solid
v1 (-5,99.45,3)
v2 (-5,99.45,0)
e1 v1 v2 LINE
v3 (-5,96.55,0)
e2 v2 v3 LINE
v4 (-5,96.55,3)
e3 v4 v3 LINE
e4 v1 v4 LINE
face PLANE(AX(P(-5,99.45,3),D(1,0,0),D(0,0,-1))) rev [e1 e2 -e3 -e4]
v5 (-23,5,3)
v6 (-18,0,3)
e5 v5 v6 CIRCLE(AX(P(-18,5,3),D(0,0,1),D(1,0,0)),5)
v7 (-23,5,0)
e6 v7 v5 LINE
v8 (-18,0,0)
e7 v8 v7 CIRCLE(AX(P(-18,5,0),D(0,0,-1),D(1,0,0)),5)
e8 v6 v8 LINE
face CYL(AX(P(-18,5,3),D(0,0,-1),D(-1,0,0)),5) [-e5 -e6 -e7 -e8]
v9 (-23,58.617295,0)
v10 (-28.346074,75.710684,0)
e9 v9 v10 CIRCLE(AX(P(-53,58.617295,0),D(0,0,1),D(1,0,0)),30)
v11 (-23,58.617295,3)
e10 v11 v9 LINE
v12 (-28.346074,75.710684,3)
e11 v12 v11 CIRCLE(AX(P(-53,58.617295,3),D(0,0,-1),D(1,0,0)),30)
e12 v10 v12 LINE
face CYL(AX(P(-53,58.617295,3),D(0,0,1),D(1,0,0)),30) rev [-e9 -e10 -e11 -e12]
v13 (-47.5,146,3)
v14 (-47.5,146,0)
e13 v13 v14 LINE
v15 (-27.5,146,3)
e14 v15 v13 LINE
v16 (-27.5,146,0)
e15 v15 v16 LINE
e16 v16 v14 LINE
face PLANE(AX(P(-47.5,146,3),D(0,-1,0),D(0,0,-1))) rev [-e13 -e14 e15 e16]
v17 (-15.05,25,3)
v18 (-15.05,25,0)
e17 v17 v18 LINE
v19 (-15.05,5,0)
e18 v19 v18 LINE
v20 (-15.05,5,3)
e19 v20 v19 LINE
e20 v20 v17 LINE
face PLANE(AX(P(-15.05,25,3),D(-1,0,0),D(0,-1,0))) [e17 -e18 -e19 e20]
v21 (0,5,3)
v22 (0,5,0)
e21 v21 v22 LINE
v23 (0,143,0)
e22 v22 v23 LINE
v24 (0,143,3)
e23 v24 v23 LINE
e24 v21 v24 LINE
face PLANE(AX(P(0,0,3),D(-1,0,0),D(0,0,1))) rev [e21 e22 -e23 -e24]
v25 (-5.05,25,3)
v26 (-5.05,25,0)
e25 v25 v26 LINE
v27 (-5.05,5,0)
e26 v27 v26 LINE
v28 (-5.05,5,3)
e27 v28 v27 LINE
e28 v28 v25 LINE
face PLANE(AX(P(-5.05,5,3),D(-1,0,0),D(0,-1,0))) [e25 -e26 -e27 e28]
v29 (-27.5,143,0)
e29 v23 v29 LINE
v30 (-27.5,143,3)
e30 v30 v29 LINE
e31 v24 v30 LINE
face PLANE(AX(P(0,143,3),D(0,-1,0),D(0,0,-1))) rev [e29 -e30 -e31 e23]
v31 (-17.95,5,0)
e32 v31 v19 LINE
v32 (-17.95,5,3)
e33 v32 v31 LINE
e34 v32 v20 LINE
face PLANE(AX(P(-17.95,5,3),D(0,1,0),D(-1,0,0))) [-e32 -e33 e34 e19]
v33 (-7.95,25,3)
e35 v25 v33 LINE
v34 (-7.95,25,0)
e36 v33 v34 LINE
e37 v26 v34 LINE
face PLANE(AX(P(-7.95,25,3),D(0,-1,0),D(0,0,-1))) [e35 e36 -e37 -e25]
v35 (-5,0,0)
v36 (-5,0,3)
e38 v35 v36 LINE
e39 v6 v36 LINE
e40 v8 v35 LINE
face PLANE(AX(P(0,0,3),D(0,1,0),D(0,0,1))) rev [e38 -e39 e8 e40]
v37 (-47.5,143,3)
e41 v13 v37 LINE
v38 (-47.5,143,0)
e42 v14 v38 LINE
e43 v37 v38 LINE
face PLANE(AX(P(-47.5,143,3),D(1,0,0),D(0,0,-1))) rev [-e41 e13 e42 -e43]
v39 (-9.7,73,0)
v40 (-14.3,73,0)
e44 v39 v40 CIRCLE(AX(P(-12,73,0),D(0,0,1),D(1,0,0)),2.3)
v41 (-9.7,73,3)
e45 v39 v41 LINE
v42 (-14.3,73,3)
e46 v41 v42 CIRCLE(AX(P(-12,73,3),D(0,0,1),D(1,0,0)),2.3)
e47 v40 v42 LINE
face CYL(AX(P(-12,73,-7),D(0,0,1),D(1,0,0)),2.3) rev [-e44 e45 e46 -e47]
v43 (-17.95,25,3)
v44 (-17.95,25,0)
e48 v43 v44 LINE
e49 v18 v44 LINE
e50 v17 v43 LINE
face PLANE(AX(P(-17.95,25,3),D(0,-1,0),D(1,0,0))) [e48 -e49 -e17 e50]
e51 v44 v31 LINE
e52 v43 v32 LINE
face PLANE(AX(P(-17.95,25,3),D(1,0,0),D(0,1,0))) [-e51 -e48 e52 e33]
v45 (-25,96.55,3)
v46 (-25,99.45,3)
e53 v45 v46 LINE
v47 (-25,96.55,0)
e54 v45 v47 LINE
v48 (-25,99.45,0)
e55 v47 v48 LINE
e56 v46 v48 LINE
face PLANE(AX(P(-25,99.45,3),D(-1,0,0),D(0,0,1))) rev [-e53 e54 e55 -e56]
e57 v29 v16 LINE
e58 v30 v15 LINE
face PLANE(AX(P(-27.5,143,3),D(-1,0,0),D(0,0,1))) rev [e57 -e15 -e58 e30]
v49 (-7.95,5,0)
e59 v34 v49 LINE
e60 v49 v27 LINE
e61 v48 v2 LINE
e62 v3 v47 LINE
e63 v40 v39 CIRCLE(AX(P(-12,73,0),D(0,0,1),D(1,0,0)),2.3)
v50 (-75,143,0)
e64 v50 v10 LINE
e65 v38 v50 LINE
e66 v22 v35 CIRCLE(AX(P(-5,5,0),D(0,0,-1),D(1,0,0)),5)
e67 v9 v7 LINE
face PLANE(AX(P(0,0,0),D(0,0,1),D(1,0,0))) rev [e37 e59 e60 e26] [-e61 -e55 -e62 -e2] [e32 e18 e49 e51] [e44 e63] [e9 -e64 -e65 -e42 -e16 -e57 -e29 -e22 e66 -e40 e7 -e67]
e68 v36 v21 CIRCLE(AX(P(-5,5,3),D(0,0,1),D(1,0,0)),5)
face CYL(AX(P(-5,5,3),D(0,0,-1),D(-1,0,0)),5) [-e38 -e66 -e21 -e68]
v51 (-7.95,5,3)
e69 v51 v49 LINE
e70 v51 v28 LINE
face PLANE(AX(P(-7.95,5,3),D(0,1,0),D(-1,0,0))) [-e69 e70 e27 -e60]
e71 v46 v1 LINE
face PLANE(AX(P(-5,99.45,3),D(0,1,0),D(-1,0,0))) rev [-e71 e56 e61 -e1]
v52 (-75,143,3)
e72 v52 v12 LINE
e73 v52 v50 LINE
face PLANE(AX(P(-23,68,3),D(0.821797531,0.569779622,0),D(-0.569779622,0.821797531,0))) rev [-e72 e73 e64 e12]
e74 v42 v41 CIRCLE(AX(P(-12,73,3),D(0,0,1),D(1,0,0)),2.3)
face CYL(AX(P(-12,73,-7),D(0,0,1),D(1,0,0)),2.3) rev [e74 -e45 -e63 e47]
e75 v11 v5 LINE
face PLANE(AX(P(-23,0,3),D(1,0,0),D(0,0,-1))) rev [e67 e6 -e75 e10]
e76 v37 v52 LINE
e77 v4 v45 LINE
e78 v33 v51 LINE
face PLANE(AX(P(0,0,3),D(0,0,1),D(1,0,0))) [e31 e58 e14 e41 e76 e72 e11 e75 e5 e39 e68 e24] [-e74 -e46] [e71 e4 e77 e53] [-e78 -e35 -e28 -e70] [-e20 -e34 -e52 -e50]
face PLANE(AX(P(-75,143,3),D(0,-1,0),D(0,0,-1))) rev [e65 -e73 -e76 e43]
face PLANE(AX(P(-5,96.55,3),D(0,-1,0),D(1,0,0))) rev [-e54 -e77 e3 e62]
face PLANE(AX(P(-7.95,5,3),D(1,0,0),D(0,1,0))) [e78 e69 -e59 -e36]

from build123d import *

# Parameters (mm, degrees)
SKETCH1_W           = 2.9
SKETCH1_H           = 20
BOSS_EXTRUDE1_DEPTH = 3
FILLET1_R           = 5
FILLET2_R           = 30
SKETCH4_R           = 2.3
CUT_EXTRUDE1_DEPTH  = 10
SKETCH5_W           = 20
SKETCH5_H           = 2.9
CUT_EXTRUDE2_DEPTH  = 165.164551594


with BuildPart() as part:
    # Sketch1 → Boss-Extrude1 (new body)
    with BuildSketch(Plane.XY):
        Polygon((0, 0), (-23, 0), (-23, 68), (-75, 143), (-47.5, 143), (-47.5, 146), (-27.5, 146), (-27.5, 143), (0, 143), align=None)
        with Locations((-16.5, 15)):
            Rectangle(SKETCH1_W, SKETCH1_H, mode=Mode.SUBTRACT)
        with Locations((-6.5, 15)):
            Rectangle(SKETCH1_W, SKETCH1_H, mode=Mode.SUBTRACT)
    extrude(amount=BOSS_EXTRUDE1_DEPTH)

    # Fillet1
    fillet1_edges = [part.edges().sort_by_distance(p)[0] for p in [
        (0, 0, 1.5),
        (-23, 0, 1.5),
    ]]
    fillet(fillet1_edges, radius=FILLET1_R)

    # Fillet2
    fillet2_edges = [part.edges().sort_by_distance(p)[0] for p in [
        (-23, 68, 1.5),
    ]]
    fillet(fillet2_edges, radius=FILLET2_R)

    # Sketch4 → Cut-Extrude1 (cut)
    with BuildSketch(Plane.XY.offset(3)):
        with Locations((-12, 73)):
            Circle(SKETCH4_R)
    extrude(amount=-CUT_EXTRUDE1_DEPTH, mode=Mode.SUBTRACT)

    # Sketch5 → Cut-Extrude2 (cut, through all)
    with BuildSketch(Plane(origin=(0, 0, 0), x_dir=(-1, 0, 0), z_dir=(0, 0, -1))):
        with Locations((15, 98)):
            Rectangle(SKETCH5_W, SKETCH5_H)
    extrude(amount=-CUT_EXTRUDE2_DEPTH, mode=Mode.SUBTRACT)


solid = part.part
